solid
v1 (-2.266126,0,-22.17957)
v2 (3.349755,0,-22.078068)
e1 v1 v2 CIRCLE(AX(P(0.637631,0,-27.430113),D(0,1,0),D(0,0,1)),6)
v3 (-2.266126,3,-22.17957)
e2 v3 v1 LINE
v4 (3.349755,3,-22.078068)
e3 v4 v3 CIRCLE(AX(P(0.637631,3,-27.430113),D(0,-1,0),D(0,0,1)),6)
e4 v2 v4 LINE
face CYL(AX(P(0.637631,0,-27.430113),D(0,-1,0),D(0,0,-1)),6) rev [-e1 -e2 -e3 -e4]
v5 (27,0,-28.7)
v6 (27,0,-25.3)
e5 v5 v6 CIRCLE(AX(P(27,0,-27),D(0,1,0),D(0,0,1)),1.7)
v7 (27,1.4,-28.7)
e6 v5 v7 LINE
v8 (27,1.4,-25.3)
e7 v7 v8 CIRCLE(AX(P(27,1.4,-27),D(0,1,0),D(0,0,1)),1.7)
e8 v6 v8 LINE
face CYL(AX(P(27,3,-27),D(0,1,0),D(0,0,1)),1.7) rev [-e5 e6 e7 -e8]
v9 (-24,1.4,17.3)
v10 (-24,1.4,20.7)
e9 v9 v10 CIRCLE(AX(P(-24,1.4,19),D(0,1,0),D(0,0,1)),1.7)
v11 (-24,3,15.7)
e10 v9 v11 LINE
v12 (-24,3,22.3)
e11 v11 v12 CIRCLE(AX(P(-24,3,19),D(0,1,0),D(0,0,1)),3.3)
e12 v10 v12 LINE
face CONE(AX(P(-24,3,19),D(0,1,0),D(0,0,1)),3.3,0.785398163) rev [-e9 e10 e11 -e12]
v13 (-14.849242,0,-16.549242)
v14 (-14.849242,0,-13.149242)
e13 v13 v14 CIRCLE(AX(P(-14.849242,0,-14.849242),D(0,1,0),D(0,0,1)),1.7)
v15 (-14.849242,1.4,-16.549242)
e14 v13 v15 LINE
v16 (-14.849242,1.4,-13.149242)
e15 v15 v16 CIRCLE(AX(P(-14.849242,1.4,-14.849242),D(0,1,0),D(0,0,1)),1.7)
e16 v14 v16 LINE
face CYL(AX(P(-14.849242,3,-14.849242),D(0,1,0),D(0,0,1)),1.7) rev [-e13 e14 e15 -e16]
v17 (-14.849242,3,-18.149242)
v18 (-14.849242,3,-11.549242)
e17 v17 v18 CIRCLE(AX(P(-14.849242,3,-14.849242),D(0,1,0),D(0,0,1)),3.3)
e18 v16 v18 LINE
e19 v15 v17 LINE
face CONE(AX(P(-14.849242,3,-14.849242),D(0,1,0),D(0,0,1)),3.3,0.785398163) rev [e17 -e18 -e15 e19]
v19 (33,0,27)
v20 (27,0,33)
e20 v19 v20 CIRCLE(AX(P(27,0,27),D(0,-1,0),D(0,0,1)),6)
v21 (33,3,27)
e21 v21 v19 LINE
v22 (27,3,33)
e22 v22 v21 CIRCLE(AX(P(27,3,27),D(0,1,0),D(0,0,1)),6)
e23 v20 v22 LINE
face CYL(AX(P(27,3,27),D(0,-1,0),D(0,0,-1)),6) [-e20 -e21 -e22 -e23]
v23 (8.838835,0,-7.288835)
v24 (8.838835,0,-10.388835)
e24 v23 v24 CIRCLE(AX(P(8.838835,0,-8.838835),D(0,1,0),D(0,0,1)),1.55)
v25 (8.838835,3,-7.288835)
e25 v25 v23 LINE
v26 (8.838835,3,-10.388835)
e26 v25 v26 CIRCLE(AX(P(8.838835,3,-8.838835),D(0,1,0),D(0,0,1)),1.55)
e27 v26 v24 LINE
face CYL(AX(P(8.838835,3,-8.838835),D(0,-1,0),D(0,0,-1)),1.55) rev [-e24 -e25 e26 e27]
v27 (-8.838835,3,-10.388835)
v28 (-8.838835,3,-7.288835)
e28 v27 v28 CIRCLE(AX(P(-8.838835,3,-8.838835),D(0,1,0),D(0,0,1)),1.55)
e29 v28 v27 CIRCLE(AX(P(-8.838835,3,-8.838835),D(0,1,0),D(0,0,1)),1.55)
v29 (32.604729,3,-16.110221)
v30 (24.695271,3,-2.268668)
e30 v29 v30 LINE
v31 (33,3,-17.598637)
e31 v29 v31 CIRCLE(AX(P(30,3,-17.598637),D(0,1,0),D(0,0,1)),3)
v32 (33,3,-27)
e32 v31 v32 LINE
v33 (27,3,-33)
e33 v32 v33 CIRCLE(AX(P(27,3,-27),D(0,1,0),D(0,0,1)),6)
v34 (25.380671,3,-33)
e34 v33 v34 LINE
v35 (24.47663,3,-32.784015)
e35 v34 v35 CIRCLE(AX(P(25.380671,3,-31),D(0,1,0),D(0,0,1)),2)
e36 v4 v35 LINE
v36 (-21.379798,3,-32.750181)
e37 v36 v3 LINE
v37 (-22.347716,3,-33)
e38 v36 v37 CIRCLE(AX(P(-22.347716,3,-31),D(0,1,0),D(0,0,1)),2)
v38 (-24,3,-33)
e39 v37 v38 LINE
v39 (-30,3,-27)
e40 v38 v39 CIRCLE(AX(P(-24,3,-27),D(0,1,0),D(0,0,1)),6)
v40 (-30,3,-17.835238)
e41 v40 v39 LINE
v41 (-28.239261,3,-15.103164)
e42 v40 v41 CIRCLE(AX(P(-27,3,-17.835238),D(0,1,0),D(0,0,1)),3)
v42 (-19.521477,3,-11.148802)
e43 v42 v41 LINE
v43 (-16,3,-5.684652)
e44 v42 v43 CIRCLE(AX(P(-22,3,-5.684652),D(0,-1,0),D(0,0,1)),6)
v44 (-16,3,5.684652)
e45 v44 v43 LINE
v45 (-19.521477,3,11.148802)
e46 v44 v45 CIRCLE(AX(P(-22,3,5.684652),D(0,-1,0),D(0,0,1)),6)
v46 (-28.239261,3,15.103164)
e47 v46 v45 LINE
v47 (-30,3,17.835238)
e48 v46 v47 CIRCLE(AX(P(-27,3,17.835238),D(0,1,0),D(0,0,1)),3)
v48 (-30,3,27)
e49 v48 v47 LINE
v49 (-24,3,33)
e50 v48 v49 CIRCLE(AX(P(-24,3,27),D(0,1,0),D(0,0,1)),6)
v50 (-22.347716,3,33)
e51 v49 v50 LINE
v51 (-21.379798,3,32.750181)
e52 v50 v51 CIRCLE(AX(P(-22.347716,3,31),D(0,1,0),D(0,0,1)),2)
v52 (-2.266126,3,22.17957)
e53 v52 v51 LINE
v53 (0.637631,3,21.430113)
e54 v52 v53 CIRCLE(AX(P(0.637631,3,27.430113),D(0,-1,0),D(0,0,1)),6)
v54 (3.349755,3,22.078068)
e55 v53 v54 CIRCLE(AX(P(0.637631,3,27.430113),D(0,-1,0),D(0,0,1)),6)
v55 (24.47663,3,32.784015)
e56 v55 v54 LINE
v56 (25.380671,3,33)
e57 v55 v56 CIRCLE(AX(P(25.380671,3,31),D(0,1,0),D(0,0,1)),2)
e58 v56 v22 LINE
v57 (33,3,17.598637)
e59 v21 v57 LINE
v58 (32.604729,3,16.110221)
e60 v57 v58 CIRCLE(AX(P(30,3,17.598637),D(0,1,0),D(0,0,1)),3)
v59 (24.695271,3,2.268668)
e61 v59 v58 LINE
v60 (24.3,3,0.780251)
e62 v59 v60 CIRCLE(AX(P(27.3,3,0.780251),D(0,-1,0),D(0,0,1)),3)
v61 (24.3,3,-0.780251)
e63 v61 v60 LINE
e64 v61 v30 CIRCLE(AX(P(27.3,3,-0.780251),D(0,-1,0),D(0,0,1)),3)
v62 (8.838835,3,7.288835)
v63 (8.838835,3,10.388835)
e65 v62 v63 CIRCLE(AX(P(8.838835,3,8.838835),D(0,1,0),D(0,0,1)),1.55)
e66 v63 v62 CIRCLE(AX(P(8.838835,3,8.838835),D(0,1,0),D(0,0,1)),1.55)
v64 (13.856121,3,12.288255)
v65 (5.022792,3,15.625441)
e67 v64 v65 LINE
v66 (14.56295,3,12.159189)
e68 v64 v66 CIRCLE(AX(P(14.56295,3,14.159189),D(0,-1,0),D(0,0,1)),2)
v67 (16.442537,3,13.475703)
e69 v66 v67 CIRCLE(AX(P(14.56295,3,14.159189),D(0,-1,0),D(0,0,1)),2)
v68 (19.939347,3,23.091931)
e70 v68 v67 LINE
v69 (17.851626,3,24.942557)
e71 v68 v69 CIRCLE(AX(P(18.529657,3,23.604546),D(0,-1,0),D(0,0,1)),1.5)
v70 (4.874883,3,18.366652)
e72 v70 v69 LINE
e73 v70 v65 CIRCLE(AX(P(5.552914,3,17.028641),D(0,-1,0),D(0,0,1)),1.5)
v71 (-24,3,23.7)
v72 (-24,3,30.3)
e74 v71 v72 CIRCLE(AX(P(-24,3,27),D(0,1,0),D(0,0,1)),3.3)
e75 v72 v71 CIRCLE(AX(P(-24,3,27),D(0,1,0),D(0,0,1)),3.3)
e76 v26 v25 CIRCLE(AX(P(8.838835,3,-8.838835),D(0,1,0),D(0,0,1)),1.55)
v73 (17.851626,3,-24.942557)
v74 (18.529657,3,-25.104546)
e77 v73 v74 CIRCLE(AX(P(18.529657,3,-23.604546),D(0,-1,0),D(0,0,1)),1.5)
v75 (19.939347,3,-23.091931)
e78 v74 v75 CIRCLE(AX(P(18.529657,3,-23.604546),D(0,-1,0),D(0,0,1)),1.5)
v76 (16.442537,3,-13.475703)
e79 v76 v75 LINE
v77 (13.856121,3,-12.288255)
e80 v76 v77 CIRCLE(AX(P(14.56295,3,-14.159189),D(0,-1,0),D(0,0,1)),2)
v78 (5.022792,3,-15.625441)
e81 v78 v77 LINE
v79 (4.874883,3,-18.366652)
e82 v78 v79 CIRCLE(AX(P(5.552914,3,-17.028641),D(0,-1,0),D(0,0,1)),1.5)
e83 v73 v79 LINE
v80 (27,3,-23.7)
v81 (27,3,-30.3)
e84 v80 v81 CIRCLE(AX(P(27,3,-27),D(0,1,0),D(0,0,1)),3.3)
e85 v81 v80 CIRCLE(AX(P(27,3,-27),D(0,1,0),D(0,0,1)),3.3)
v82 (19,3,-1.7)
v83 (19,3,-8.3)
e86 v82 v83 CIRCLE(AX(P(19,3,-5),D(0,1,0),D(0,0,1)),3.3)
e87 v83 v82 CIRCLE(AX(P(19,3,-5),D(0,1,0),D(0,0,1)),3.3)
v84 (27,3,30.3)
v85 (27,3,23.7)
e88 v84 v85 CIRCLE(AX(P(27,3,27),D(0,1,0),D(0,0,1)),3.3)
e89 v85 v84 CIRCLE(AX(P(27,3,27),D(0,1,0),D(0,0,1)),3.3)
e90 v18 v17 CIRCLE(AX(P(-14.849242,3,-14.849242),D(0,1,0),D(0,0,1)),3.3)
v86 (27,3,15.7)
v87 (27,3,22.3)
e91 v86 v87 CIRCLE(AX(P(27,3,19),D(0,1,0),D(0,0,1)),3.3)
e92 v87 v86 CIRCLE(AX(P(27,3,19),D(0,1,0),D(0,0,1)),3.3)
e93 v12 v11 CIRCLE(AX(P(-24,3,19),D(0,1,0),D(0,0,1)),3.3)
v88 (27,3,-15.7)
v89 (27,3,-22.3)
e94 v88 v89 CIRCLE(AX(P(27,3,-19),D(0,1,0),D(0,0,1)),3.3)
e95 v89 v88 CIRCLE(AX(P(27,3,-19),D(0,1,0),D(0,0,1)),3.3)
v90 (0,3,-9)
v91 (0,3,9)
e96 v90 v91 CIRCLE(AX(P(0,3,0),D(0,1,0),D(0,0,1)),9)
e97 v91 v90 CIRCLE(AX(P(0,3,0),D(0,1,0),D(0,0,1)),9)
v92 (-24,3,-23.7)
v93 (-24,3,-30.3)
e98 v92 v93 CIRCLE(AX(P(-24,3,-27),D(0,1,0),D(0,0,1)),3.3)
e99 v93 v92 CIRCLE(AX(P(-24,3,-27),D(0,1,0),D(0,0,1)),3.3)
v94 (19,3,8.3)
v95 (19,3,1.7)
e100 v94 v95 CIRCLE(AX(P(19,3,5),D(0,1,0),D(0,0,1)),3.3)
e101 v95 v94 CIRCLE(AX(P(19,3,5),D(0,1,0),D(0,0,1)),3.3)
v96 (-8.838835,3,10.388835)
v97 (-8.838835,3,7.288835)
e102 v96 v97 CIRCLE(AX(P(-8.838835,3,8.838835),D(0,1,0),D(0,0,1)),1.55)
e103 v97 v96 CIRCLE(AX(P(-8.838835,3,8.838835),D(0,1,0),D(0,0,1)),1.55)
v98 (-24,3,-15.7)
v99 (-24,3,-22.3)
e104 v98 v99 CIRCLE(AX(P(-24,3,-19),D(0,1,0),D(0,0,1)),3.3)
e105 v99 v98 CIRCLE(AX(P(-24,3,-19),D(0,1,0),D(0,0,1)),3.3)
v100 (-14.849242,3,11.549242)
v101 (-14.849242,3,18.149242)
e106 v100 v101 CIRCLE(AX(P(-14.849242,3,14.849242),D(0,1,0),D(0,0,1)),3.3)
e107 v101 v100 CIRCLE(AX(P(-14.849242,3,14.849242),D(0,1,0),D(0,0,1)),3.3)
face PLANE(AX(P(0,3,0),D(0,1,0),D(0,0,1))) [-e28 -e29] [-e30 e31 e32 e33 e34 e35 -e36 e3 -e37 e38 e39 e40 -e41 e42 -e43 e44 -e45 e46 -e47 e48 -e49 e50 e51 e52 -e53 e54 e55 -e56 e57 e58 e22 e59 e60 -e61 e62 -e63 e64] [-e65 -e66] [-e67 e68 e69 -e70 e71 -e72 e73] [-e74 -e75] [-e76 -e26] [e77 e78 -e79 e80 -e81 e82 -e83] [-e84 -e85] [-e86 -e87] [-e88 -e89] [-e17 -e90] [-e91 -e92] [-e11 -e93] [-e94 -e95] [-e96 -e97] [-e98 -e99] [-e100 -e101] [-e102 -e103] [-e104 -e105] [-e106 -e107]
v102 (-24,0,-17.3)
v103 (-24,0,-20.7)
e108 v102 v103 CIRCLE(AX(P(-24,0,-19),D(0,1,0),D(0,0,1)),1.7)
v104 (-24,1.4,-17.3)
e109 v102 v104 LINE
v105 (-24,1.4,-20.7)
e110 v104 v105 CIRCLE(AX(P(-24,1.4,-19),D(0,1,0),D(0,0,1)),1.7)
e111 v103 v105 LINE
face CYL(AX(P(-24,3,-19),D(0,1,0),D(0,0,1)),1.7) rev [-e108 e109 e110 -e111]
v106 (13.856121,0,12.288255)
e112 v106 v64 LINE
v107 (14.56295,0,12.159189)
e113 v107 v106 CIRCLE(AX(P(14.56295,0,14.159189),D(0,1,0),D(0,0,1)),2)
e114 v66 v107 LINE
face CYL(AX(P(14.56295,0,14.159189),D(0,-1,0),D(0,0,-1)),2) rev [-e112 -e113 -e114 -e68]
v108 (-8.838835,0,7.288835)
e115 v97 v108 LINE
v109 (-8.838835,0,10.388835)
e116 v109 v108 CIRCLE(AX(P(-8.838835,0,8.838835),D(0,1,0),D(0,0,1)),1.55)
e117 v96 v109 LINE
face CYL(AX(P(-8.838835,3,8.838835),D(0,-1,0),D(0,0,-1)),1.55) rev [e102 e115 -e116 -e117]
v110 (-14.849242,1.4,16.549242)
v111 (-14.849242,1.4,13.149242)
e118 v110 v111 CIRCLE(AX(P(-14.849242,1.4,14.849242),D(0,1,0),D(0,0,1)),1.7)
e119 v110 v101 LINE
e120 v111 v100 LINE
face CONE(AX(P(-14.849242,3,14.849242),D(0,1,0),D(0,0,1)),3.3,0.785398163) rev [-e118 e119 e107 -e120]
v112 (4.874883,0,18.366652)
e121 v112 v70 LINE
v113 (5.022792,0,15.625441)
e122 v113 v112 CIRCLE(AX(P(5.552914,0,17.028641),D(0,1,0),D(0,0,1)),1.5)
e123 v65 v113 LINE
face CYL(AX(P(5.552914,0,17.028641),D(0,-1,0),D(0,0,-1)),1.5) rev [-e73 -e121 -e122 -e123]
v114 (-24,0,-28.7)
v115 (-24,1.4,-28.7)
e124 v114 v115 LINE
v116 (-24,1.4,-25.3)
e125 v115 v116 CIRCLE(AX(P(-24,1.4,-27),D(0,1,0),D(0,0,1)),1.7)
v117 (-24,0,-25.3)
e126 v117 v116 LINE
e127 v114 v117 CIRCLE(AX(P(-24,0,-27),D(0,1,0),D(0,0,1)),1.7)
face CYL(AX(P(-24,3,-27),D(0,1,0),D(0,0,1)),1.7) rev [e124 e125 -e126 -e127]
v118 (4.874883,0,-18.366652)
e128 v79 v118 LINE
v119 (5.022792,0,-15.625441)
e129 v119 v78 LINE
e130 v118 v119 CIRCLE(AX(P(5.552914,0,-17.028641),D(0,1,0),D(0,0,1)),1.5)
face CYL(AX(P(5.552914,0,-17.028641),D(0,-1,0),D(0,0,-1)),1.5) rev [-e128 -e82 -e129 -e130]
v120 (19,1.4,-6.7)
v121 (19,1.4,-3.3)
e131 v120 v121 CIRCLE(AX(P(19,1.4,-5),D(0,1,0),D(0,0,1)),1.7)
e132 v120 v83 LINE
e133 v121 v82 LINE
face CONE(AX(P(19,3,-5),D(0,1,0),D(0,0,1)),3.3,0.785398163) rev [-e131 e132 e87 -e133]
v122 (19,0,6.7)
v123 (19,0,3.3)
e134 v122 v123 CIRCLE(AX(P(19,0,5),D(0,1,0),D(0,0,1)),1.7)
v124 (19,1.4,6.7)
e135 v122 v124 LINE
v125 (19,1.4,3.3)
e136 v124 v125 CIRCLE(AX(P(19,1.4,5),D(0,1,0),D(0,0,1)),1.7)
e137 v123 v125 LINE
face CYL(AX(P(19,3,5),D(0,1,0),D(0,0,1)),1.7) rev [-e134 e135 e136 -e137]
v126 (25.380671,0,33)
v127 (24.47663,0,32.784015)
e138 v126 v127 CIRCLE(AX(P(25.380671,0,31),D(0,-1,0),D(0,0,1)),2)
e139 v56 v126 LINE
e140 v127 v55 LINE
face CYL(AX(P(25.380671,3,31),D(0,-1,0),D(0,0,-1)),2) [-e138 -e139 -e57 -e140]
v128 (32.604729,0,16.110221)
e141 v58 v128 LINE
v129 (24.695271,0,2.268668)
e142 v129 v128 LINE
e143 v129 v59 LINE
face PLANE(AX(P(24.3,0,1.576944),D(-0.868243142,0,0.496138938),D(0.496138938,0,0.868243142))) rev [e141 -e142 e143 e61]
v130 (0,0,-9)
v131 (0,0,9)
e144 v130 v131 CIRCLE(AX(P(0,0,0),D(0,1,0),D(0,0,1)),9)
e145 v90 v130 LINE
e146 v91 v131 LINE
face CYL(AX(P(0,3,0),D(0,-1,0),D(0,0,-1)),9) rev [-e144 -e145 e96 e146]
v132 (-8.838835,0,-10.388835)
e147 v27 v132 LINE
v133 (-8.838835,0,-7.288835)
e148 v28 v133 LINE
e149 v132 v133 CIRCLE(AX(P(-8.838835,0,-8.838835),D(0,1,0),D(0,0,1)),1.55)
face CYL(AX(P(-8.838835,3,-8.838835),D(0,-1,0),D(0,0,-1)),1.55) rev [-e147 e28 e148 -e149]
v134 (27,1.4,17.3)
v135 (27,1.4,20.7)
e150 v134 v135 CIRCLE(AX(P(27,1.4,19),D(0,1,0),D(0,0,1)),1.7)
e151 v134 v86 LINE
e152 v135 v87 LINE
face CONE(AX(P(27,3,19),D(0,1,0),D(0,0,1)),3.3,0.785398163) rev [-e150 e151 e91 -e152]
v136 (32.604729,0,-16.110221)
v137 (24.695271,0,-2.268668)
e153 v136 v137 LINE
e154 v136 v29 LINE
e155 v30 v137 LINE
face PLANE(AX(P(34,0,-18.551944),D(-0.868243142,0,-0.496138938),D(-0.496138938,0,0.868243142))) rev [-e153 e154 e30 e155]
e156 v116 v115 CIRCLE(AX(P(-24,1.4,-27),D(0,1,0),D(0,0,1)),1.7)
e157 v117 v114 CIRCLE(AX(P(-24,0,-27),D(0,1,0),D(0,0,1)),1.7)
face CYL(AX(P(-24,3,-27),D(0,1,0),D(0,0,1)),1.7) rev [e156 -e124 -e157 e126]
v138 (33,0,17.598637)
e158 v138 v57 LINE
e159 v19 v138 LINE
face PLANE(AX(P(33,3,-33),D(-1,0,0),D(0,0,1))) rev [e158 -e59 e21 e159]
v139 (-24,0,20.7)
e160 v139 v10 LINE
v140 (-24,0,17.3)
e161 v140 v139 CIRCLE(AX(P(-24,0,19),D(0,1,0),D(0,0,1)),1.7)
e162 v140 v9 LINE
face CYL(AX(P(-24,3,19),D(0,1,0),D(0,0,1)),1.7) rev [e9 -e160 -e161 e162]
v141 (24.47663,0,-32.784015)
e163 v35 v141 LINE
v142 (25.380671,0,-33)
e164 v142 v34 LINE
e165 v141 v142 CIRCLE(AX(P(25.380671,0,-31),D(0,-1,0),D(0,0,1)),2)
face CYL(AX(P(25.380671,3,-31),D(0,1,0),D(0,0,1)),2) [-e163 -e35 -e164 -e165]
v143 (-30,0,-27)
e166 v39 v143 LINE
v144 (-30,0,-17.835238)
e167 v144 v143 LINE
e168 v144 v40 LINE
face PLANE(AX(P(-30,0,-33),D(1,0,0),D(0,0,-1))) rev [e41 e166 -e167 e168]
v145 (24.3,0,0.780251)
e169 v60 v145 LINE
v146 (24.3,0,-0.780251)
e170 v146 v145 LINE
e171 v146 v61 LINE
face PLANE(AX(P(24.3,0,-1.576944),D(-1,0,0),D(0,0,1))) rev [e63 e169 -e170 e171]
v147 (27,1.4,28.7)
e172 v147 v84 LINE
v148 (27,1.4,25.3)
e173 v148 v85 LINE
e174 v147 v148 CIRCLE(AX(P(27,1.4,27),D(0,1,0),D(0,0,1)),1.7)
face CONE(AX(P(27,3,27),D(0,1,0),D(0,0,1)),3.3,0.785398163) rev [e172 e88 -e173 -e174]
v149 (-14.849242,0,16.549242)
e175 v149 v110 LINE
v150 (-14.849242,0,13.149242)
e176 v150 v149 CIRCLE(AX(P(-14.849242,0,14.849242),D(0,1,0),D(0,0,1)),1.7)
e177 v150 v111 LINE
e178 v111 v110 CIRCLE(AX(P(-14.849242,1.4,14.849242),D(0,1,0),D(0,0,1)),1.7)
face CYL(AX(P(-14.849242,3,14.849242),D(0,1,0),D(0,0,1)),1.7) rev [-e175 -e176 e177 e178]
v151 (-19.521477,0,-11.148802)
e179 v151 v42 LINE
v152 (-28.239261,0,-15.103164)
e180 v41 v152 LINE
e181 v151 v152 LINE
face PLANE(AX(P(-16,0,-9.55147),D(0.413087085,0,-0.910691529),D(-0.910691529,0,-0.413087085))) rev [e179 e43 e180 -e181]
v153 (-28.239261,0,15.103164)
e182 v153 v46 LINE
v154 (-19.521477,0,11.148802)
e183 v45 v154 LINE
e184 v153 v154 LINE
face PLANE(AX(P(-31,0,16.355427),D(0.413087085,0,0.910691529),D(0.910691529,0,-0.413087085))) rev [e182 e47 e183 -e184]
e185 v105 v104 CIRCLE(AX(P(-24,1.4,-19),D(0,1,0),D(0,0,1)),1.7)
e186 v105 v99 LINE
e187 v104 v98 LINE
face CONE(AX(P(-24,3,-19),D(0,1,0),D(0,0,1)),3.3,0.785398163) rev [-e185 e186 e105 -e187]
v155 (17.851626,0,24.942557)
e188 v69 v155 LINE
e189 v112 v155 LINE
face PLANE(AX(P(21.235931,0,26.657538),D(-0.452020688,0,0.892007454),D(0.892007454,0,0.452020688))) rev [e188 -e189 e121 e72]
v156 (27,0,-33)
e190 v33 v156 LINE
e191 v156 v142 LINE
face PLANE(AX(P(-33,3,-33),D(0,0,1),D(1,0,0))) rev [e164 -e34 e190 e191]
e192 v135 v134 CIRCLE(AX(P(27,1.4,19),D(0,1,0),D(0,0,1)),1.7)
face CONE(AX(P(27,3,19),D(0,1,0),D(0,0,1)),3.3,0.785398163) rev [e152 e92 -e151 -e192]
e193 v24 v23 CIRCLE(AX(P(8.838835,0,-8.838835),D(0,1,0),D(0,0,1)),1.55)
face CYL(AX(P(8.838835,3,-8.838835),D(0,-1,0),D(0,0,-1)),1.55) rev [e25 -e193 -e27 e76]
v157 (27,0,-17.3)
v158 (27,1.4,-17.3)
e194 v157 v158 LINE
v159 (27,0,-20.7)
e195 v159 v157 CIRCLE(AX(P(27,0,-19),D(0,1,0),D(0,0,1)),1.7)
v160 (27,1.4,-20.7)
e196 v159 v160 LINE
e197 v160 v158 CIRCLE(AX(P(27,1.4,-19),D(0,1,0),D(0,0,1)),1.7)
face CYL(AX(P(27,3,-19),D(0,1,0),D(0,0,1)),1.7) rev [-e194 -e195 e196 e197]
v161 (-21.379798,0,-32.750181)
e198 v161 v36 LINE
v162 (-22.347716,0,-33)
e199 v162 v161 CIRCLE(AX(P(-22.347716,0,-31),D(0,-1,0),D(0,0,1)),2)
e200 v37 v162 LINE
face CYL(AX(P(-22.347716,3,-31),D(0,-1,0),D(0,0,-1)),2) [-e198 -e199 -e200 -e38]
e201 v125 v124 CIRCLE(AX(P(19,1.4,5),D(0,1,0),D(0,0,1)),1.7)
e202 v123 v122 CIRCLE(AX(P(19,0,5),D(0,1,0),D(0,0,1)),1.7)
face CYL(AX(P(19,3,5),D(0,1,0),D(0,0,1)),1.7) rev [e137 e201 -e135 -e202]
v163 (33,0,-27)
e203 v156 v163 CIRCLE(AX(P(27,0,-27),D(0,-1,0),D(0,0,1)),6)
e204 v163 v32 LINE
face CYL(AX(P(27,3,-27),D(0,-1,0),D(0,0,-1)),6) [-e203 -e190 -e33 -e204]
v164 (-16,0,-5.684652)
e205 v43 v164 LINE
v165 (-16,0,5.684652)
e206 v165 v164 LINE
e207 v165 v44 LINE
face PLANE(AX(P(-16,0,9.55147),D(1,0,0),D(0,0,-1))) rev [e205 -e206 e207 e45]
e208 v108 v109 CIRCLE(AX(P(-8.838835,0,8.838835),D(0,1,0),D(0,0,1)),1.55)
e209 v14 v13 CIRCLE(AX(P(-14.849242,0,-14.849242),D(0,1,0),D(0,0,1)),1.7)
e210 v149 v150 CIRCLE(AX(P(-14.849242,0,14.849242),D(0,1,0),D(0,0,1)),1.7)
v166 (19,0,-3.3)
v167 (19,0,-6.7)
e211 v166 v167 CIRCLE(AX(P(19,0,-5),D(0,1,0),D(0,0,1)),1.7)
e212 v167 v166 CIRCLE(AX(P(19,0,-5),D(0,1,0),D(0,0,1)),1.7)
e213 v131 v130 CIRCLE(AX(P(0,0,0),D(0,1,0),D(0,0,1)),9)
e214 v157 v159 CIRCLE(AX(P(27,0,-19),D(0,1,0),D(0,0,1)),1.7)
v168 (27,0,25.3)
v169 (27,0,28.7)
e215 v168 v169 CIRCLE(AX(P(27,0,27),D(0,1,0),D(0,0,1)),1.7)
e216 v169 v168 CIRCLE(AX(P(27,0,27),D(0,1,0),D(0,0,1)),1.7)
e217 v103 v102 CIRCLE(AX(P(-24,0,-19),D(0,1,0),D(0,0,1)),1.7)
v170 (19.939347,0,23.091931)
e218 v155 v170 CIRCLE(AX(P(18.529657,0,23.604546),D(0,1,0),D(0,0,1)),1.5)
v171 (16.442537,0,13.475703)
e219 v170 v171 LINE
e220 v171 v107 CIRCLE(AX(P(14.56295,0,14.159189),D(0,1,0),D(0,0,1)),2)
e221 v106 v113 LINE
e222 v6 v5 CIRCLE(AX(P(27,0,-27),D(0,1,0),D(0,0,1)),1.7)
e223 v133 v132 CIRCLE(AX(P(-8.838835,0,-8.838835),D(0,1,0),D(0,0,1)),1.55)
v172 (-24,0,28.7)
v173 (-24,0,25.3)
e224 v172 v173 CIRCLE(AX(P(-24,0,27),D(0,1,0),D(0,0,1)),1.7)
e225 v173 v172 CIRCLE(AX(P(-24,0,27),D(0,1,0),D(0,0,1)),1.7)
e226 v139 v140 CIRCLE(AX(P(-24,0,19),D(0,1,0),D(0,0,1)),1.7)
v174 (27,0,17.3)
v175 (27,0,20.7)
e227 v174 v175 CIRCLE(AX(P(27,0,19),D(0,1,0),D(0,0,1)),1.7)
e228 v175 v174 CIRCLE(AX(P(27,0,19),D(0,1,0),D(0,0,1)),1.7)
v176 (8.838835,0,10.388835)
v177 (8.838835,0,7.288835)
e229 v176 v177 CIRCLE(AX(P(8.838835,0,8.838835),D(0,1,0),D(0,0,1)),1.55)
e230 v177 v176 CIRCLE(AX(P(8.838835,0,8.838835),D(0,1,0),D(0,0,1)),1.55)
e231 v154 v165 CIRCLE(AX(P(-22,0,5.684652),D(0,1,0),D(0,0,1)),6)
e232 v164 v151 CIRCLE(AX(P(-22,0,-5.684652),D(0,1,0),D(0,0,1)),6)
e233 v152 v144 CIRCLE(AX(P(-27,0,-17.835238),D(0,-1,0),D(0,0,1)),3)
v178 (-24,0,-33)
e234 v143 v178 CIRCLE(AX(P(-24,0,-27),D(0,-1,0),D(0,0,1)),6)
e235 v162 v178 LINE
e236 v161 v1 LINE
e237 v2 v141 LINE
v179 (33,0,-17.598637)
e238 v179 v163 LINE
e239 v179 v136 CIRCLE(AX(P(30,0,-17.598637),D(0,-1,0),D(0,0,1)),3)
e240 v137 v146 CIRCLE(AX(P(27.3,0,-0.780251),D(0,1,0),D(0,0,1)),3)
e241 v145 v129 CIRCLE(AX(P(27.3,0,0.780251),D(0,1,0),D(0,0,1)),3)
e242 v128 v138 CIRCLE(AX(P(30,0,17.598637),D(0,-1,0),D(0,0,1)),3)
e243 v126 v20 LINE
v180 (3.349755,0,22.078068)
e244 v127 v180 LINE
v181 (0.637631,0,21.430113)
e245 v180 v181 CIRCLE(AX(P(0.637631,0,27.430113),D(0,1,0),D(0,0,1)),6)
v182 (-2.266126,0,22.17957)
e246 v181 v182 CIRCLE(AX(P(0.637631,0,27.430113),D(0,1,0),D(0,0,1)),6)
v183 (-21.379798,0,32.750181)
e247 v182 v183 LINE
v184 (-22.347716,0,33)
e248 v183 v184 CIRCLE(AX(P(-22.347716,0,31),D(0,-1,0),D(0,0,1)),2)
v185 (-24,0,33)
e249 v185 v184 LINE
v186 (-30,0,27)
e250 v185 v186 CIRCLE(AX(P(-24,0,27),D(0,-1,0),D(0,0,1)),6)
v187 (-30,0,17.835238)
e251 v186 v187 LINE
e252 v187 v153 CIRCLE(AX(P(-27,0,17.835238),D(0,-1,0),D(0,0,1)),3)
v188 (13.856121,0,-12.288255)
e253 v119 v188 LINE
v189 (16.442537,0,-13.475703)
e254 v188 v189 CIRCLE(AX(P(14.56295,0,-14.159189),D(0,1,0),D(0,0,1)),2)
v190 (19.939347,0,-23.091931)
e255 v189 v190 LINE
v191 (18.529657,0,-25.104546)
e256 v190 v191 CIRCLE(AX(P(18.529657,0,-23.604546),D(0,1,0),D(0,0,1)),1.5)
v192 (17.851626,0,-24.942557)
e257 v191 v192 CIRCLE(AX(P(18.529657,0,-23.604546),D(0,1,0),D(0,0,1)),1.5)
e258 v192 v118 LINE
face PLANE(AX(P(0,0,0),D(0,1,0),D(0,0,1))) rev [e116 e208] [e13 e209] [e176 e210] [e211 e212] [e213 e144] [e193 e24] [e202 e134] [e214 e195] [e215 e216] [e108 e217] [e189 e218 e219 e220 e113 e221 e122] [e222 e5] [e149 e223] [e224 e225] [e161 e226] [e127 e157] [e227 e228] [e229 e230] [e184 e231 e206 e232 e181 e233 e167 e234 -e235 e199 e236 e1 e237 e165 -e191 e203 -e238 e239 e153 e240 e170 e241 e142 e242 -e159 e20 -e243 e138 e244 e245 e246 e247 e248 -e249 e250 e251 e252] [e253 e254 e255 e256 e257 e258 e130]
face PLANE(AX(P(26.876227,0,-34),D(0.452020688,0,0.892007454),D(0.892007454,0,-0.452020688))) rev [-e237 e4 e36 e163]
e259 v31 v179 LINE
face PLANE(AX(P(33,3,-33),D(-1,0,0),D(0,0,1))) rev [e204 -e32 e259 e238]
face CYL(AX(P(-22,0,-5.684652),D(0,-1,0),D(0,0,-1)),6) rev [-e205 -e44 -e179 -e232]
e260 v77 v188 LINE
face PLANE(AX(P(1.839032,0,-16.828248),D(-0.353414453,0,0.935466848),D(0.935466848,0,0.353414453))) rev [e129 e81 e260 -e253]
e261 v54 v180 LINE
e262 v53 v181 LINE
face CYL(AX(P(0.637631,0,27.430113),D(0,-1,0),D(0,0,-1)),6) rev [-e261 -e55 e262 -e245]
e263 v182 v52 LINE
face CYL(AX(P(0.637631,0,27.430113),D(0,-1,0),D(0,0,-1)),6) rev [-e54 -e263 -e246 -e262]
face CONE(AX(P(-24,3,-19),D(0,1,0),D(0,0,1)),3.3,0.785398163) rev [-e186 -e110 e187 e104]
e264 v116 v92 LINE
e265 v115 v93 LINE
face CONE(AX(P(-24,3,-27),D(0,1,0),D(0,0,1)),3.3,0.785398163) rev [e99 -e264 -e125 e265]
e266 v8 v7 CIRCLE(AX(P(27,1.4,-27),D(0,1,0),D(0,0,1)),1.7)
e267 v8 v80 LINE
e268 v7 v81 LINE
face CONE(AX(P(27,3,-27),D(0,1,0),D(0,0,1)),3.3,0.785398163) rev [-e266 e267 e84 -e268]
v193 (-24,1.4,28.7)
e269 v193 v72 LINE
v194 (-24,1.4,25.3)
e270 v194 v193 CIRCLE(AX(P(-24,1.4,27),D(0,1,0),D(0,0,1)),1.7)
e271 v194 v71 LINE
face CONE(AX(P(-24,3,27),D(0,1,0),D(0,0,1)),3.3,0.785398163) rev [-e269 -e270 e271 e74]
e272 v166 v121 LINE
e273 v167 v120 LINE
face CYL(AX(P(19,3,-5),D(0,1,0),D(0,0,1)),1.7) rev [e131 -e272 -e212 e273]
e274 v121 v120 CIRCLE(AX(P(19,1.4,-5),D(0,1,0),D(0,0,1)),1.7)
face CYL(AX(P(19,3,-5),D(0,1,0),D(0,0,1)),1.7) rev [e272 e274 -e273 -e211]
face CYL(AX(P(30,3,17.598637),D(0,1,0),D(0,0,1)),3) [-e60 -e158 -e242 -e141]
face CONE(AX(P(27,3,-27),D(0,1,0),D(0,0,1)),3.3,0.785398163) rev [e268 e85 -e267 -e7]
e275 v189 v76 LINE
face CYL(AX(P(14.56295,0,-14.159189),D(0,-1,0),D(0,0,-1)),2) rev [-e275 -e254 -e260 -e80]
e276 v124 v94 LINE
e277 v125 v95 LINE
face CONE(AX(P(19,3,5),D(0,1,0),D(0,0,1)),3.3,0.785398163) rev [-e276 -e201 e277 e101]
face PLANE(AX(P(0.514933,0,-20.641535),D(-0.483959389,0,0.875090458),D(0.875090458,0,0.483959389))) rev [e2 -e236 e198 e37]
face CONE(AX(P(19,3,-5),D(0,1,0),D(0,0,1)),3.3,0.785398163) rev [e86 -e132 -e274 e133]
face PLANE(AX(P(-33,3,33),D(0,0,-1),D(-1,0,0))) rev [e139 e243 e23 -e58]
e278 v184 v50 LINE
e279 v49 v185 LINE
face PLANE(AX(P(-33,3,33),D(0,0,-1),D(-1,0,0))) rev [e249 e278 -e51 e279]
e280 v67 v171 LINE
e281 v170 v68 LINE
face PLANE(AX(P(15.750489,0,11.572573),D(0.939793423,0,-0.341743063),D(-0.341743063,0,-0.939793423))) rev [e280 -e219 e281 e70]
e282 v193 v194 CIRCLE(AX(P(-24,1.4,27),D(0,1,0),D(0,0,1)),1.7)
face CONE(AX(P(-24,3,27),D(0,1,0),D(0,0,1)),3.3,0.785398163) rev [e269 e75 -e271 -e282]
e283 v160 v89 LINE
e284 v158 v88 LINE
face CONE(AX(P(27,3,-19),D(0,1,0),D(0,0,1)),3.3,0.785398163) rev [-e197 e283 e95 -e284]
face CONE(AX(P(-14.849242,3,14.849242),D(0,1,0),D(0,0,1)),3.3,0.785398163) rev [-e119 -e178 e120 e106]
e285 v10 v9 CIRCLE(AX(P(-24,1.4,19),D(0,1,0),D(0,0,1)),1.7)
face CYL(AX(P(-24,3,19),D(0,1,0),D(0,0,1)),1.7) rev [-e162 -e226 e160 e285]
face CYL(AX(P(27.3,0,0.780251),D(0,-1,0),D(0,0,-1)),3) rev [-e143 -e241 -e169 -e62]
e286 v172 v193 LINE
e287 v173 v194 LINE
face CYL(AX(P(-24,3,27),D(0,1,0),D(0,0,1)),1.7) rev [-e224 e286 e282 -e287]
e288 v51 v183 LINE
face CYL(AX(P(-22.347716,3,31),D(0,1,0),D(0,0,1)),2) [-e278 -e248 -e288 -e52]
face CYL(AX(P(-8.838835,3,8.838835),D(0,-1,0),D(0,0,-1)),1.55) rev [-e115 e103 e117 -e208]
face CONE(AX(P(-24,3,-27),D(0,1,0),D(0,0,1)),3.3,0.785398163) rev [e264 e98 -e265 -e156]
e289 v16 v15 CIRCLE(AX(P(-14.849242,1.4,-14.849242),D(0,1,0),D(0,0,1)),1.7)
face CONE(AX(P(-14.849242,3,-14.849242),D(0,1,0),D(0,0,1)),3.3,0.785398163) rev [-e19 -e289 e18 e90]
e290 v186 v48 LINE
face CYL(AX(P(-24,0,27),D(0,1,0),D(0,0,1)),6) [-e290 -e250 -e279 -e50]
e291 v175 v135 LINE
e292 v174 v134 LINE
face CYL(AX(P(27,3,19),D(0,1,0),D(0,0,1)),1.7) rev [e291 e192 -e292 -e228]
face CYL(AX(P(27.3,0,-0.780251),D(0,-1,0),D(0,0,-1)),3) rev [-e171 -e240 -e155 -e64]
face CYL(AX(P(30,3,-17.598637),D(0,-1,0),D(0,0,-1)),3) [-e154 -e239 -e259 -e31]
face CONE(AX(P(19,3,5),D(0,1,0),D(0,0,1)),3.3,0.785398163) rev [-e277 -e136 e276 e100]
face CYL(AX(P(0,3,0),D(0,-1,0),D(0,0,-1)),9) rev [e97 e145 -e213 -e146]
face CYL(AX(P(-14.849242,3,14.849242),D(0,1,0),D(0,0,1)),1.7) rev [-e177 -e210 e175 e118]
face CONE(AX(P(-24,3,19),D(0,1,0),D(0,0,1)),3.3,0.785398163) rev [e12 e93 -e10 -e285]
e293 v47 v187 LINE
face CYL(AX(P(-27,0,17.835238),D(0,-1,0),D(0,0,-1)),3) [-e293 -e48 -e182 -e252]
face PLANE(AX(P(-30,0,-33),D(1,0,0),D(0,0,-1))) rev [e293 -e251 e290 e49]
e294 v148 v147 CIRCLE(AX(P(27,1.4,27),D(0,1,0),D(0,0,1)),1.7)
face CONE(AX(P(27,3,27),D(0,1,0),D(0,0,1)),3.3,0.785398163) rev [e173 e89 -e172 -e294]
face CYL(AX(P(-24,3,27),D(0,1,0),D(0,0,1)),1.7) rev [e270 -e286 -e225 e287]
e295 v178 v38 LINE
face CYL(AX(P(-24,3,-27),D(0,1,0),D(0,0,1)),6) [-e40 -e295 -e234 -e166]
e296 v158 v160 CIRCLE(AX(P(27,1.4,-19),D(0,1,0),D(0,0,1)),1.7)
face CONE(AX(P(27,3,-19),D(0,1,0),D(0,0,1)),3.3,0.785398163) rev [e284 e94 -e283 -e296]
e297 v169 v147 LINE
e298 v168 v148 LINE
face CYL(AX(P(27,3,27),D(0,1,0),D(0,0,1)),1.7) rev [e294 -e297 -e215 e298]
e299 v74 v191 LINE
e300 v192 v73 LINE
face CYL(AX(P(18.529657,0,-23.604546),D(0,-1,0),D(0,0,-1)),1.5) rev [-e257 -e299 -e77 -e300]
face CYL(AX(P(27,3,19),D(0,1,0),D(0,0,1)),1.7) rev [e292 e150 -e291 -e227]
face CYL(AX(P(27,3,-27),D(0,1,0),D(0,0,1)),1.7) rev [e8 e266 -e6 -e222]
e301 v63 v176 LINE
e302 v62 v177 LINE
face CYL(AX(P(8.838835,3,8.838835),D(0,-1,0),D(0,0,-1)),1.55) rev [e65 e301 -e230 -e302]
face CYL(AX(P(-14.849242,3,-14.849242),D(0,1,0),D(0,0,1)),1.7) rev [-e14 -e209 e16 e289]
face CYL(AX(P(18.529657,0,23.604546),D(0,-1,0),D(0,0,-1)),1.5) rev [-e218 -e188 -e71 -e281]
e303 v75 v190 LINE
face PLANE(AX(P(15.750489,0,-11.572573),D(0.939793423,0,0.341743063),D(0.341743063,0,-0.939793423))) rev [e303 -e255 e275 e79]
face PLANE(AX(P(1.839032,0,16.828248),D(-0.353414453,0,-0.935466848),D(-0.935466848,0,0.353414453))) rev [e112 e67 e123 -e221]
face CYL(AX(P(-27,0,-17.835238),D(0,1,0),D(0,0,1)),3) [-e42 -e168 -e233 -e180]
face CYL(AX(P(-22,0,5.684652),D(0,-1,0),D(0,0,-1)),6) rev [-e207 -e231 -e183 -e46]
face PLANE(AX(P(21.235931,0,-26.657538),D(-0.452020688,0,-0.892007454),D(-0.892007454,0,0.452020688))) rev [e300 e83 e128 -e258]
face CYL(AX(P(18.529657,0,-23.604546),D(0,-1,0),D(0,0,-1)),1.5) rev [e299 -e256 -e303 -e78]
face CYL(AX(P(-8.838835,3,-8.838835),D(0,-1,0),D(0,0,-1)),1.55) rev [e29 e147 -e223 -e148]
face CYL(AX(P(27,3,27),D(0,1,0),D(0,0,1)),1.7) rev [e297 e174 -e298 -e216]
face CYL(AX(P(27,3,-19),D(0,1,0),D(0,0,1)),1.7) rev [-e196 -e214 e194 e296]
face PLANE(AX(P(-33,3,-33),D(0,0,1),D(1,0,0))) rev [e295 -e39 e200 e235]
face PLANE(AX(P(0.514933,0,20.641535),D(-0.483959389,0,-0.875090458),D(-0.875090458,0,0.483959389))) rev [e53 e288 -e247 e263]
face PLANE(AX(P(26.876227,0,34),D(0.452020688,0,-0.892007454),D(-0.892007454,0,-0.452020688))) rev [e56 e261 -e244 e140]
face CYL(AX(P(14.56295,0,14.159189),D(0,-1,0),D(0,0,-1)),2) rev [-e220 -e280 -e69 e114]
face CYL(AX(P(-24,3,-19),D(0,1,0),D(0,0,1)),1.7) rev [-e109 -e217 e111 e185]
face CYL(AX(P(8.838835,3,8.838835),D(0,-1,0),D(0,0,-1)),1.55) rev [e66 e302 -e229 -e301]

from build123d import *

# Parameters (mm, degrees)
SKETCH_1_W                   = 66
SKETCH_1_H                   = 66
SKETCH_1_R                   = 9
SKETCH_1_R_2                 = 1.55
EXTRUDE_1_DEPTH              = 3
HOLE_WIZARD_M3_1_D           = 3.4
HOLE_WIZARD_M3_1_DEPTH       = 7.5
HOLE_WIZARD_M3_1_CSINK_D     = 6.6
HOLE_WIZARD_M3_1_CSINK_ANGLE = 90
HOLE_WIZARD_M3_1_TIP         = 1.021463052
CUT_EXTRUDE_3_DEPTH          = 47.765371804
CUT_EXTRUDE_3_DEPTH_BACK     = 47.765371804
SKETCH_8_W                   = 3
SKETCH_8_H                   = 66
FILLET_1_R                   = 6
CUT_EXTRUDE_2_DEPTH          = 47.765371804
FILLET_2_R                   = 2
FILLET_3_R                   = 1.5
FILLET_4_R                   = 6
FILLET_5_R                   = 3


with BuildPart() as part:
    # 草图1 → 凸台-拉伸1 (new body)
    with BuildSketch(Plane(origin=(0, 0, 0), x_dir=(1, 0, 0), z_dir=(0, 1, 0))):
        Rectangle(SKETCH_1_W, SKETCH_1_H)
        with Locations(Location((0, 0, 0), (0, 0, 270))):
            Circle(SKETCH_1_R, mode=Mode.SUBTRACT)
        with Locations(Location((-24, 19, 0), (0, 0, 270))):
            Circle(SKETCH_1_R_2, mode=Mode.SUBTRACT)
        with Locations(Location((-24, 27, 0), (0, 0, 270))):
            Circle(SKETCH_1_R_2, mode=Mode.SUBTRACT)
        with Locations(Location((-24, -19, 0), (0, 0, 90))):
            Circle(SKETCH_1_R_2, mode=Mode.SUBTRACT)
        with Locations(Location((-24, -27, 0), (0, 0, 90))):
            Circle(SKETCH_1_R_2, mode=Mode.SUBTRACT)
        with Locations(Location((-14.849242405, 14.849242405, 0), (0, 0, 270))):
            Circle(SKETCH_1_R_2, mode=Mode.SUBTRACT)
        with Locations(Location((19, 5, 0), (0, 0, 270))):
            Circle(SKETCH_1_R_2, mode=Mode.SUBTRACT)
        with Locations(Location((19, -5, 0), (0, 0, 90))):
            Circle(SKETCH_1_R_2, mode=Mode.SUBTRACT)
        with Locations(Location((-14.849242405, -14.849242405, 0), (0, 0, 90))):
            Circle(SKETCH_1_R_2, mode=Mode.SUBTRACT)
        with Locations(Location((8.838834765, 8.838834765, 0), (0, 0, 270))):
            Circle(SKETCH_1_R_2, mode=Mode.SUBTRACT)
        with Locations(Location((8.838834765, -8.838834765, 0), (0, 0, 270))):
            Circle(SKETCH_1_R_2, mode=Mode.SUBTRACT)
        with Locations(Location((-8.838834765, -8.838834765, 0), (0, 0, 270))):
            Circle(SKETCH_1_R_2, mode=Mode.SUBTRACT)
        with Locations(Location((-8.838834765, 8.838834765, 0), (0, 0, 270))):
            Circle(SKETCH_1_R_2, mode=Mode.SUBTRACT)
        with Locations(Location((27, 27, 0), (0, 0, 270))):
            Circle(SKETCH_1_R_2, mode=Mode.SUBTRACT)
        with Locations(Location((27, 19, 0), (0, 0, 270))):
            Circle(SKETCH_1_R_2, mode=Mode.SUBTRACT)
        with Locations(Location((27, -19, 0), (0, 0, 90))):
            Circle(SKETCH_1_R_2, mode=Mode.SUBTRACT)
        with Locations(Location((27, -27, 0), (0, 0, 90))):
            Circle(SKETCH_1_R_2, mode=Mode.SUBTRACT)
    extrude(amount=EXTRUDE_1_DEPTH)

    # M3 十字槽半沉头木螺钉的锥形沉头孔1
    with Locations(Plane(origin=(0, 3, 0), x_dir=(1, 0, 0), z_dir=(0, 1, 0))):
        with Locations((-24, 27), (-24, 19), (-24, -19), (-24, -27), (-14.849242405, 14.849242405), (-14.849242405, -14.849242405), (19, -5), (19, 5), (27, 19), (27, 27), (27, -19), (27, -27)):
            CounterSinkHole(HOLE_WIZARD_M3_1_D / 2, HOLE_WIZARD_M3_1_CSINK_D / 2, depth=HOLE_WIZARD_M3_1_DEPTH, counter_sink_angle=HOLE_WIZARD_M3_1_CSINK_ANGLE)
            with Locations((0, 0, -(HOLE_WIZARD_M3_1_DEPTH + HOLE_WIZARD_M3_1_TIP / 2))):  # 118° drill point
                Cone(0, HOLE_WIZARD_M3_1_D / 2, HOLE_WIZARD_M3_1_TIP, mode=Mode.SUBTRACT)

    # 草图8 → 切除-拉伸3 (cut, two sides: drawn at the far end of the back side and taken through both)
    with BuildSketch(Plane(origin=(0, 3, 0), x_dir=(1, 0, 0), z_dir=(0, 1, 0)).offset(-CUT_EXTRUDE_3_DEPTH_BACK)):
        with Locations((-31.5, 0)):
            Rectangle(SKETCH_8_W, SKETCH_8_H)
    extrude(amount=CUT_EXTRUDE_3_DEPTH + CUT_EXTRUDE_3_DEPTH_BACK, mode=Mode.SUBTRACT)

    # 圆角1
    fillet_1_edges = [part.edges().sort_by_distance(p)[0] for p in [
        (-30, 1.5, -33),
        (-30, 1.5, 33),
        (33, 1.5, 33),
        (33, 1.5, -33),
    ]]
    fillet(fillet_1_edges, radius=FILLET_1_R)

    # 草图5 → 切除-拉伸2 (cut, through all)
    with BuildSketch(Plane(origin=(0, 3, 0), x_dir=(1, 0, 0), z_dir=(0, 1, 0))):
        Polygon((-31, 16.355426805), (-31, -16.355426805), (-16, -9.551469506), (-16, 9.551469506), align=None)
        Polygon((34, 18.551944046), (24.3, 1.576944046), (24.3, -1.576944046), (34, -18.551944046), align=None)
        Polygon((-23.639707799, 34), (26.876227293, 34), (0.514933103, 20.641535007), align=None)
        Polygon((21.235931274, 26.657538386), (1.839031633, 16.828248406), (15.750489279, 11.5725729), align=None)
        Polygon((1.839031633, -16.828248406), (15.750489279, -11.5725729), (21.235931274, -26.657538386), align=None)
        Polygon((26.876227293, -34), (0.514933103, -20.641535007), (-23.639707799, -34), align=None)
    extrude(amount=-CUT_EXTRUDE_2_DEPTH, mode=Mode.SUBTRACT)

    # 圆角2
    fillet_2_edges = [part.edges().sort_by_distance(p)[0] for p in [
        (24.902849797, 1.5, 33),
        (-21.831517943, 1.5, 33),
        (-21.831517943, 1.5, -33),
        (24.902849797, 1.5, -33),
        (15.750489279, 1.5, 11.5725729),
        (15.750489279, 1.5, -11.5725729),
    ]]
    fillet(fillet_2_edges, radius=FILLET_2_R)

    # 圆角3
    fillet_3_edges = [part.edges().sort_by_distance(p)[0] for p in [
        (21.235931274, 1.5, 26.657538386),
        (1.839031633, 1.5, 16.828248406),
        (21.235931274, 1.5, -26.657538386),
        (1.839031633, 1.5, -16.828248406),
    ]]
    fillet(fillet_3_edges, radius=FILLET_3_R)

    # 圆角4
    fillet_4_edges = [part.edges().sort_by_distance(p)[0] for p in [
        (0.514933103, 1.5, -20.641535007),
        (0.514933103, 1.5, 20.641535007),
        (-16, 1.5, 9.551469506),
        (-16, 1.5, -9.551469506),
    ]]
    fillet(fillet_4_edges, radius=FILLET_4_R)

    # 圆角5
    fillet_5_edges = [part.edges().sort_by_distance(p)[0] for p in [
        (-30, 1.5, -15.901829651),
        (-30, 1.5, 15.901829651),
        (33, 1.5, 16.801944046),
        (33, 1.5, -16.801944046),
        (24.3, 1.5, -1.576944046),
        (24.3, 1.5, 1.576944046),
    ]]
    fillet(fillet_5_edges, radius=FILLET_5_R)


solid = part.part
